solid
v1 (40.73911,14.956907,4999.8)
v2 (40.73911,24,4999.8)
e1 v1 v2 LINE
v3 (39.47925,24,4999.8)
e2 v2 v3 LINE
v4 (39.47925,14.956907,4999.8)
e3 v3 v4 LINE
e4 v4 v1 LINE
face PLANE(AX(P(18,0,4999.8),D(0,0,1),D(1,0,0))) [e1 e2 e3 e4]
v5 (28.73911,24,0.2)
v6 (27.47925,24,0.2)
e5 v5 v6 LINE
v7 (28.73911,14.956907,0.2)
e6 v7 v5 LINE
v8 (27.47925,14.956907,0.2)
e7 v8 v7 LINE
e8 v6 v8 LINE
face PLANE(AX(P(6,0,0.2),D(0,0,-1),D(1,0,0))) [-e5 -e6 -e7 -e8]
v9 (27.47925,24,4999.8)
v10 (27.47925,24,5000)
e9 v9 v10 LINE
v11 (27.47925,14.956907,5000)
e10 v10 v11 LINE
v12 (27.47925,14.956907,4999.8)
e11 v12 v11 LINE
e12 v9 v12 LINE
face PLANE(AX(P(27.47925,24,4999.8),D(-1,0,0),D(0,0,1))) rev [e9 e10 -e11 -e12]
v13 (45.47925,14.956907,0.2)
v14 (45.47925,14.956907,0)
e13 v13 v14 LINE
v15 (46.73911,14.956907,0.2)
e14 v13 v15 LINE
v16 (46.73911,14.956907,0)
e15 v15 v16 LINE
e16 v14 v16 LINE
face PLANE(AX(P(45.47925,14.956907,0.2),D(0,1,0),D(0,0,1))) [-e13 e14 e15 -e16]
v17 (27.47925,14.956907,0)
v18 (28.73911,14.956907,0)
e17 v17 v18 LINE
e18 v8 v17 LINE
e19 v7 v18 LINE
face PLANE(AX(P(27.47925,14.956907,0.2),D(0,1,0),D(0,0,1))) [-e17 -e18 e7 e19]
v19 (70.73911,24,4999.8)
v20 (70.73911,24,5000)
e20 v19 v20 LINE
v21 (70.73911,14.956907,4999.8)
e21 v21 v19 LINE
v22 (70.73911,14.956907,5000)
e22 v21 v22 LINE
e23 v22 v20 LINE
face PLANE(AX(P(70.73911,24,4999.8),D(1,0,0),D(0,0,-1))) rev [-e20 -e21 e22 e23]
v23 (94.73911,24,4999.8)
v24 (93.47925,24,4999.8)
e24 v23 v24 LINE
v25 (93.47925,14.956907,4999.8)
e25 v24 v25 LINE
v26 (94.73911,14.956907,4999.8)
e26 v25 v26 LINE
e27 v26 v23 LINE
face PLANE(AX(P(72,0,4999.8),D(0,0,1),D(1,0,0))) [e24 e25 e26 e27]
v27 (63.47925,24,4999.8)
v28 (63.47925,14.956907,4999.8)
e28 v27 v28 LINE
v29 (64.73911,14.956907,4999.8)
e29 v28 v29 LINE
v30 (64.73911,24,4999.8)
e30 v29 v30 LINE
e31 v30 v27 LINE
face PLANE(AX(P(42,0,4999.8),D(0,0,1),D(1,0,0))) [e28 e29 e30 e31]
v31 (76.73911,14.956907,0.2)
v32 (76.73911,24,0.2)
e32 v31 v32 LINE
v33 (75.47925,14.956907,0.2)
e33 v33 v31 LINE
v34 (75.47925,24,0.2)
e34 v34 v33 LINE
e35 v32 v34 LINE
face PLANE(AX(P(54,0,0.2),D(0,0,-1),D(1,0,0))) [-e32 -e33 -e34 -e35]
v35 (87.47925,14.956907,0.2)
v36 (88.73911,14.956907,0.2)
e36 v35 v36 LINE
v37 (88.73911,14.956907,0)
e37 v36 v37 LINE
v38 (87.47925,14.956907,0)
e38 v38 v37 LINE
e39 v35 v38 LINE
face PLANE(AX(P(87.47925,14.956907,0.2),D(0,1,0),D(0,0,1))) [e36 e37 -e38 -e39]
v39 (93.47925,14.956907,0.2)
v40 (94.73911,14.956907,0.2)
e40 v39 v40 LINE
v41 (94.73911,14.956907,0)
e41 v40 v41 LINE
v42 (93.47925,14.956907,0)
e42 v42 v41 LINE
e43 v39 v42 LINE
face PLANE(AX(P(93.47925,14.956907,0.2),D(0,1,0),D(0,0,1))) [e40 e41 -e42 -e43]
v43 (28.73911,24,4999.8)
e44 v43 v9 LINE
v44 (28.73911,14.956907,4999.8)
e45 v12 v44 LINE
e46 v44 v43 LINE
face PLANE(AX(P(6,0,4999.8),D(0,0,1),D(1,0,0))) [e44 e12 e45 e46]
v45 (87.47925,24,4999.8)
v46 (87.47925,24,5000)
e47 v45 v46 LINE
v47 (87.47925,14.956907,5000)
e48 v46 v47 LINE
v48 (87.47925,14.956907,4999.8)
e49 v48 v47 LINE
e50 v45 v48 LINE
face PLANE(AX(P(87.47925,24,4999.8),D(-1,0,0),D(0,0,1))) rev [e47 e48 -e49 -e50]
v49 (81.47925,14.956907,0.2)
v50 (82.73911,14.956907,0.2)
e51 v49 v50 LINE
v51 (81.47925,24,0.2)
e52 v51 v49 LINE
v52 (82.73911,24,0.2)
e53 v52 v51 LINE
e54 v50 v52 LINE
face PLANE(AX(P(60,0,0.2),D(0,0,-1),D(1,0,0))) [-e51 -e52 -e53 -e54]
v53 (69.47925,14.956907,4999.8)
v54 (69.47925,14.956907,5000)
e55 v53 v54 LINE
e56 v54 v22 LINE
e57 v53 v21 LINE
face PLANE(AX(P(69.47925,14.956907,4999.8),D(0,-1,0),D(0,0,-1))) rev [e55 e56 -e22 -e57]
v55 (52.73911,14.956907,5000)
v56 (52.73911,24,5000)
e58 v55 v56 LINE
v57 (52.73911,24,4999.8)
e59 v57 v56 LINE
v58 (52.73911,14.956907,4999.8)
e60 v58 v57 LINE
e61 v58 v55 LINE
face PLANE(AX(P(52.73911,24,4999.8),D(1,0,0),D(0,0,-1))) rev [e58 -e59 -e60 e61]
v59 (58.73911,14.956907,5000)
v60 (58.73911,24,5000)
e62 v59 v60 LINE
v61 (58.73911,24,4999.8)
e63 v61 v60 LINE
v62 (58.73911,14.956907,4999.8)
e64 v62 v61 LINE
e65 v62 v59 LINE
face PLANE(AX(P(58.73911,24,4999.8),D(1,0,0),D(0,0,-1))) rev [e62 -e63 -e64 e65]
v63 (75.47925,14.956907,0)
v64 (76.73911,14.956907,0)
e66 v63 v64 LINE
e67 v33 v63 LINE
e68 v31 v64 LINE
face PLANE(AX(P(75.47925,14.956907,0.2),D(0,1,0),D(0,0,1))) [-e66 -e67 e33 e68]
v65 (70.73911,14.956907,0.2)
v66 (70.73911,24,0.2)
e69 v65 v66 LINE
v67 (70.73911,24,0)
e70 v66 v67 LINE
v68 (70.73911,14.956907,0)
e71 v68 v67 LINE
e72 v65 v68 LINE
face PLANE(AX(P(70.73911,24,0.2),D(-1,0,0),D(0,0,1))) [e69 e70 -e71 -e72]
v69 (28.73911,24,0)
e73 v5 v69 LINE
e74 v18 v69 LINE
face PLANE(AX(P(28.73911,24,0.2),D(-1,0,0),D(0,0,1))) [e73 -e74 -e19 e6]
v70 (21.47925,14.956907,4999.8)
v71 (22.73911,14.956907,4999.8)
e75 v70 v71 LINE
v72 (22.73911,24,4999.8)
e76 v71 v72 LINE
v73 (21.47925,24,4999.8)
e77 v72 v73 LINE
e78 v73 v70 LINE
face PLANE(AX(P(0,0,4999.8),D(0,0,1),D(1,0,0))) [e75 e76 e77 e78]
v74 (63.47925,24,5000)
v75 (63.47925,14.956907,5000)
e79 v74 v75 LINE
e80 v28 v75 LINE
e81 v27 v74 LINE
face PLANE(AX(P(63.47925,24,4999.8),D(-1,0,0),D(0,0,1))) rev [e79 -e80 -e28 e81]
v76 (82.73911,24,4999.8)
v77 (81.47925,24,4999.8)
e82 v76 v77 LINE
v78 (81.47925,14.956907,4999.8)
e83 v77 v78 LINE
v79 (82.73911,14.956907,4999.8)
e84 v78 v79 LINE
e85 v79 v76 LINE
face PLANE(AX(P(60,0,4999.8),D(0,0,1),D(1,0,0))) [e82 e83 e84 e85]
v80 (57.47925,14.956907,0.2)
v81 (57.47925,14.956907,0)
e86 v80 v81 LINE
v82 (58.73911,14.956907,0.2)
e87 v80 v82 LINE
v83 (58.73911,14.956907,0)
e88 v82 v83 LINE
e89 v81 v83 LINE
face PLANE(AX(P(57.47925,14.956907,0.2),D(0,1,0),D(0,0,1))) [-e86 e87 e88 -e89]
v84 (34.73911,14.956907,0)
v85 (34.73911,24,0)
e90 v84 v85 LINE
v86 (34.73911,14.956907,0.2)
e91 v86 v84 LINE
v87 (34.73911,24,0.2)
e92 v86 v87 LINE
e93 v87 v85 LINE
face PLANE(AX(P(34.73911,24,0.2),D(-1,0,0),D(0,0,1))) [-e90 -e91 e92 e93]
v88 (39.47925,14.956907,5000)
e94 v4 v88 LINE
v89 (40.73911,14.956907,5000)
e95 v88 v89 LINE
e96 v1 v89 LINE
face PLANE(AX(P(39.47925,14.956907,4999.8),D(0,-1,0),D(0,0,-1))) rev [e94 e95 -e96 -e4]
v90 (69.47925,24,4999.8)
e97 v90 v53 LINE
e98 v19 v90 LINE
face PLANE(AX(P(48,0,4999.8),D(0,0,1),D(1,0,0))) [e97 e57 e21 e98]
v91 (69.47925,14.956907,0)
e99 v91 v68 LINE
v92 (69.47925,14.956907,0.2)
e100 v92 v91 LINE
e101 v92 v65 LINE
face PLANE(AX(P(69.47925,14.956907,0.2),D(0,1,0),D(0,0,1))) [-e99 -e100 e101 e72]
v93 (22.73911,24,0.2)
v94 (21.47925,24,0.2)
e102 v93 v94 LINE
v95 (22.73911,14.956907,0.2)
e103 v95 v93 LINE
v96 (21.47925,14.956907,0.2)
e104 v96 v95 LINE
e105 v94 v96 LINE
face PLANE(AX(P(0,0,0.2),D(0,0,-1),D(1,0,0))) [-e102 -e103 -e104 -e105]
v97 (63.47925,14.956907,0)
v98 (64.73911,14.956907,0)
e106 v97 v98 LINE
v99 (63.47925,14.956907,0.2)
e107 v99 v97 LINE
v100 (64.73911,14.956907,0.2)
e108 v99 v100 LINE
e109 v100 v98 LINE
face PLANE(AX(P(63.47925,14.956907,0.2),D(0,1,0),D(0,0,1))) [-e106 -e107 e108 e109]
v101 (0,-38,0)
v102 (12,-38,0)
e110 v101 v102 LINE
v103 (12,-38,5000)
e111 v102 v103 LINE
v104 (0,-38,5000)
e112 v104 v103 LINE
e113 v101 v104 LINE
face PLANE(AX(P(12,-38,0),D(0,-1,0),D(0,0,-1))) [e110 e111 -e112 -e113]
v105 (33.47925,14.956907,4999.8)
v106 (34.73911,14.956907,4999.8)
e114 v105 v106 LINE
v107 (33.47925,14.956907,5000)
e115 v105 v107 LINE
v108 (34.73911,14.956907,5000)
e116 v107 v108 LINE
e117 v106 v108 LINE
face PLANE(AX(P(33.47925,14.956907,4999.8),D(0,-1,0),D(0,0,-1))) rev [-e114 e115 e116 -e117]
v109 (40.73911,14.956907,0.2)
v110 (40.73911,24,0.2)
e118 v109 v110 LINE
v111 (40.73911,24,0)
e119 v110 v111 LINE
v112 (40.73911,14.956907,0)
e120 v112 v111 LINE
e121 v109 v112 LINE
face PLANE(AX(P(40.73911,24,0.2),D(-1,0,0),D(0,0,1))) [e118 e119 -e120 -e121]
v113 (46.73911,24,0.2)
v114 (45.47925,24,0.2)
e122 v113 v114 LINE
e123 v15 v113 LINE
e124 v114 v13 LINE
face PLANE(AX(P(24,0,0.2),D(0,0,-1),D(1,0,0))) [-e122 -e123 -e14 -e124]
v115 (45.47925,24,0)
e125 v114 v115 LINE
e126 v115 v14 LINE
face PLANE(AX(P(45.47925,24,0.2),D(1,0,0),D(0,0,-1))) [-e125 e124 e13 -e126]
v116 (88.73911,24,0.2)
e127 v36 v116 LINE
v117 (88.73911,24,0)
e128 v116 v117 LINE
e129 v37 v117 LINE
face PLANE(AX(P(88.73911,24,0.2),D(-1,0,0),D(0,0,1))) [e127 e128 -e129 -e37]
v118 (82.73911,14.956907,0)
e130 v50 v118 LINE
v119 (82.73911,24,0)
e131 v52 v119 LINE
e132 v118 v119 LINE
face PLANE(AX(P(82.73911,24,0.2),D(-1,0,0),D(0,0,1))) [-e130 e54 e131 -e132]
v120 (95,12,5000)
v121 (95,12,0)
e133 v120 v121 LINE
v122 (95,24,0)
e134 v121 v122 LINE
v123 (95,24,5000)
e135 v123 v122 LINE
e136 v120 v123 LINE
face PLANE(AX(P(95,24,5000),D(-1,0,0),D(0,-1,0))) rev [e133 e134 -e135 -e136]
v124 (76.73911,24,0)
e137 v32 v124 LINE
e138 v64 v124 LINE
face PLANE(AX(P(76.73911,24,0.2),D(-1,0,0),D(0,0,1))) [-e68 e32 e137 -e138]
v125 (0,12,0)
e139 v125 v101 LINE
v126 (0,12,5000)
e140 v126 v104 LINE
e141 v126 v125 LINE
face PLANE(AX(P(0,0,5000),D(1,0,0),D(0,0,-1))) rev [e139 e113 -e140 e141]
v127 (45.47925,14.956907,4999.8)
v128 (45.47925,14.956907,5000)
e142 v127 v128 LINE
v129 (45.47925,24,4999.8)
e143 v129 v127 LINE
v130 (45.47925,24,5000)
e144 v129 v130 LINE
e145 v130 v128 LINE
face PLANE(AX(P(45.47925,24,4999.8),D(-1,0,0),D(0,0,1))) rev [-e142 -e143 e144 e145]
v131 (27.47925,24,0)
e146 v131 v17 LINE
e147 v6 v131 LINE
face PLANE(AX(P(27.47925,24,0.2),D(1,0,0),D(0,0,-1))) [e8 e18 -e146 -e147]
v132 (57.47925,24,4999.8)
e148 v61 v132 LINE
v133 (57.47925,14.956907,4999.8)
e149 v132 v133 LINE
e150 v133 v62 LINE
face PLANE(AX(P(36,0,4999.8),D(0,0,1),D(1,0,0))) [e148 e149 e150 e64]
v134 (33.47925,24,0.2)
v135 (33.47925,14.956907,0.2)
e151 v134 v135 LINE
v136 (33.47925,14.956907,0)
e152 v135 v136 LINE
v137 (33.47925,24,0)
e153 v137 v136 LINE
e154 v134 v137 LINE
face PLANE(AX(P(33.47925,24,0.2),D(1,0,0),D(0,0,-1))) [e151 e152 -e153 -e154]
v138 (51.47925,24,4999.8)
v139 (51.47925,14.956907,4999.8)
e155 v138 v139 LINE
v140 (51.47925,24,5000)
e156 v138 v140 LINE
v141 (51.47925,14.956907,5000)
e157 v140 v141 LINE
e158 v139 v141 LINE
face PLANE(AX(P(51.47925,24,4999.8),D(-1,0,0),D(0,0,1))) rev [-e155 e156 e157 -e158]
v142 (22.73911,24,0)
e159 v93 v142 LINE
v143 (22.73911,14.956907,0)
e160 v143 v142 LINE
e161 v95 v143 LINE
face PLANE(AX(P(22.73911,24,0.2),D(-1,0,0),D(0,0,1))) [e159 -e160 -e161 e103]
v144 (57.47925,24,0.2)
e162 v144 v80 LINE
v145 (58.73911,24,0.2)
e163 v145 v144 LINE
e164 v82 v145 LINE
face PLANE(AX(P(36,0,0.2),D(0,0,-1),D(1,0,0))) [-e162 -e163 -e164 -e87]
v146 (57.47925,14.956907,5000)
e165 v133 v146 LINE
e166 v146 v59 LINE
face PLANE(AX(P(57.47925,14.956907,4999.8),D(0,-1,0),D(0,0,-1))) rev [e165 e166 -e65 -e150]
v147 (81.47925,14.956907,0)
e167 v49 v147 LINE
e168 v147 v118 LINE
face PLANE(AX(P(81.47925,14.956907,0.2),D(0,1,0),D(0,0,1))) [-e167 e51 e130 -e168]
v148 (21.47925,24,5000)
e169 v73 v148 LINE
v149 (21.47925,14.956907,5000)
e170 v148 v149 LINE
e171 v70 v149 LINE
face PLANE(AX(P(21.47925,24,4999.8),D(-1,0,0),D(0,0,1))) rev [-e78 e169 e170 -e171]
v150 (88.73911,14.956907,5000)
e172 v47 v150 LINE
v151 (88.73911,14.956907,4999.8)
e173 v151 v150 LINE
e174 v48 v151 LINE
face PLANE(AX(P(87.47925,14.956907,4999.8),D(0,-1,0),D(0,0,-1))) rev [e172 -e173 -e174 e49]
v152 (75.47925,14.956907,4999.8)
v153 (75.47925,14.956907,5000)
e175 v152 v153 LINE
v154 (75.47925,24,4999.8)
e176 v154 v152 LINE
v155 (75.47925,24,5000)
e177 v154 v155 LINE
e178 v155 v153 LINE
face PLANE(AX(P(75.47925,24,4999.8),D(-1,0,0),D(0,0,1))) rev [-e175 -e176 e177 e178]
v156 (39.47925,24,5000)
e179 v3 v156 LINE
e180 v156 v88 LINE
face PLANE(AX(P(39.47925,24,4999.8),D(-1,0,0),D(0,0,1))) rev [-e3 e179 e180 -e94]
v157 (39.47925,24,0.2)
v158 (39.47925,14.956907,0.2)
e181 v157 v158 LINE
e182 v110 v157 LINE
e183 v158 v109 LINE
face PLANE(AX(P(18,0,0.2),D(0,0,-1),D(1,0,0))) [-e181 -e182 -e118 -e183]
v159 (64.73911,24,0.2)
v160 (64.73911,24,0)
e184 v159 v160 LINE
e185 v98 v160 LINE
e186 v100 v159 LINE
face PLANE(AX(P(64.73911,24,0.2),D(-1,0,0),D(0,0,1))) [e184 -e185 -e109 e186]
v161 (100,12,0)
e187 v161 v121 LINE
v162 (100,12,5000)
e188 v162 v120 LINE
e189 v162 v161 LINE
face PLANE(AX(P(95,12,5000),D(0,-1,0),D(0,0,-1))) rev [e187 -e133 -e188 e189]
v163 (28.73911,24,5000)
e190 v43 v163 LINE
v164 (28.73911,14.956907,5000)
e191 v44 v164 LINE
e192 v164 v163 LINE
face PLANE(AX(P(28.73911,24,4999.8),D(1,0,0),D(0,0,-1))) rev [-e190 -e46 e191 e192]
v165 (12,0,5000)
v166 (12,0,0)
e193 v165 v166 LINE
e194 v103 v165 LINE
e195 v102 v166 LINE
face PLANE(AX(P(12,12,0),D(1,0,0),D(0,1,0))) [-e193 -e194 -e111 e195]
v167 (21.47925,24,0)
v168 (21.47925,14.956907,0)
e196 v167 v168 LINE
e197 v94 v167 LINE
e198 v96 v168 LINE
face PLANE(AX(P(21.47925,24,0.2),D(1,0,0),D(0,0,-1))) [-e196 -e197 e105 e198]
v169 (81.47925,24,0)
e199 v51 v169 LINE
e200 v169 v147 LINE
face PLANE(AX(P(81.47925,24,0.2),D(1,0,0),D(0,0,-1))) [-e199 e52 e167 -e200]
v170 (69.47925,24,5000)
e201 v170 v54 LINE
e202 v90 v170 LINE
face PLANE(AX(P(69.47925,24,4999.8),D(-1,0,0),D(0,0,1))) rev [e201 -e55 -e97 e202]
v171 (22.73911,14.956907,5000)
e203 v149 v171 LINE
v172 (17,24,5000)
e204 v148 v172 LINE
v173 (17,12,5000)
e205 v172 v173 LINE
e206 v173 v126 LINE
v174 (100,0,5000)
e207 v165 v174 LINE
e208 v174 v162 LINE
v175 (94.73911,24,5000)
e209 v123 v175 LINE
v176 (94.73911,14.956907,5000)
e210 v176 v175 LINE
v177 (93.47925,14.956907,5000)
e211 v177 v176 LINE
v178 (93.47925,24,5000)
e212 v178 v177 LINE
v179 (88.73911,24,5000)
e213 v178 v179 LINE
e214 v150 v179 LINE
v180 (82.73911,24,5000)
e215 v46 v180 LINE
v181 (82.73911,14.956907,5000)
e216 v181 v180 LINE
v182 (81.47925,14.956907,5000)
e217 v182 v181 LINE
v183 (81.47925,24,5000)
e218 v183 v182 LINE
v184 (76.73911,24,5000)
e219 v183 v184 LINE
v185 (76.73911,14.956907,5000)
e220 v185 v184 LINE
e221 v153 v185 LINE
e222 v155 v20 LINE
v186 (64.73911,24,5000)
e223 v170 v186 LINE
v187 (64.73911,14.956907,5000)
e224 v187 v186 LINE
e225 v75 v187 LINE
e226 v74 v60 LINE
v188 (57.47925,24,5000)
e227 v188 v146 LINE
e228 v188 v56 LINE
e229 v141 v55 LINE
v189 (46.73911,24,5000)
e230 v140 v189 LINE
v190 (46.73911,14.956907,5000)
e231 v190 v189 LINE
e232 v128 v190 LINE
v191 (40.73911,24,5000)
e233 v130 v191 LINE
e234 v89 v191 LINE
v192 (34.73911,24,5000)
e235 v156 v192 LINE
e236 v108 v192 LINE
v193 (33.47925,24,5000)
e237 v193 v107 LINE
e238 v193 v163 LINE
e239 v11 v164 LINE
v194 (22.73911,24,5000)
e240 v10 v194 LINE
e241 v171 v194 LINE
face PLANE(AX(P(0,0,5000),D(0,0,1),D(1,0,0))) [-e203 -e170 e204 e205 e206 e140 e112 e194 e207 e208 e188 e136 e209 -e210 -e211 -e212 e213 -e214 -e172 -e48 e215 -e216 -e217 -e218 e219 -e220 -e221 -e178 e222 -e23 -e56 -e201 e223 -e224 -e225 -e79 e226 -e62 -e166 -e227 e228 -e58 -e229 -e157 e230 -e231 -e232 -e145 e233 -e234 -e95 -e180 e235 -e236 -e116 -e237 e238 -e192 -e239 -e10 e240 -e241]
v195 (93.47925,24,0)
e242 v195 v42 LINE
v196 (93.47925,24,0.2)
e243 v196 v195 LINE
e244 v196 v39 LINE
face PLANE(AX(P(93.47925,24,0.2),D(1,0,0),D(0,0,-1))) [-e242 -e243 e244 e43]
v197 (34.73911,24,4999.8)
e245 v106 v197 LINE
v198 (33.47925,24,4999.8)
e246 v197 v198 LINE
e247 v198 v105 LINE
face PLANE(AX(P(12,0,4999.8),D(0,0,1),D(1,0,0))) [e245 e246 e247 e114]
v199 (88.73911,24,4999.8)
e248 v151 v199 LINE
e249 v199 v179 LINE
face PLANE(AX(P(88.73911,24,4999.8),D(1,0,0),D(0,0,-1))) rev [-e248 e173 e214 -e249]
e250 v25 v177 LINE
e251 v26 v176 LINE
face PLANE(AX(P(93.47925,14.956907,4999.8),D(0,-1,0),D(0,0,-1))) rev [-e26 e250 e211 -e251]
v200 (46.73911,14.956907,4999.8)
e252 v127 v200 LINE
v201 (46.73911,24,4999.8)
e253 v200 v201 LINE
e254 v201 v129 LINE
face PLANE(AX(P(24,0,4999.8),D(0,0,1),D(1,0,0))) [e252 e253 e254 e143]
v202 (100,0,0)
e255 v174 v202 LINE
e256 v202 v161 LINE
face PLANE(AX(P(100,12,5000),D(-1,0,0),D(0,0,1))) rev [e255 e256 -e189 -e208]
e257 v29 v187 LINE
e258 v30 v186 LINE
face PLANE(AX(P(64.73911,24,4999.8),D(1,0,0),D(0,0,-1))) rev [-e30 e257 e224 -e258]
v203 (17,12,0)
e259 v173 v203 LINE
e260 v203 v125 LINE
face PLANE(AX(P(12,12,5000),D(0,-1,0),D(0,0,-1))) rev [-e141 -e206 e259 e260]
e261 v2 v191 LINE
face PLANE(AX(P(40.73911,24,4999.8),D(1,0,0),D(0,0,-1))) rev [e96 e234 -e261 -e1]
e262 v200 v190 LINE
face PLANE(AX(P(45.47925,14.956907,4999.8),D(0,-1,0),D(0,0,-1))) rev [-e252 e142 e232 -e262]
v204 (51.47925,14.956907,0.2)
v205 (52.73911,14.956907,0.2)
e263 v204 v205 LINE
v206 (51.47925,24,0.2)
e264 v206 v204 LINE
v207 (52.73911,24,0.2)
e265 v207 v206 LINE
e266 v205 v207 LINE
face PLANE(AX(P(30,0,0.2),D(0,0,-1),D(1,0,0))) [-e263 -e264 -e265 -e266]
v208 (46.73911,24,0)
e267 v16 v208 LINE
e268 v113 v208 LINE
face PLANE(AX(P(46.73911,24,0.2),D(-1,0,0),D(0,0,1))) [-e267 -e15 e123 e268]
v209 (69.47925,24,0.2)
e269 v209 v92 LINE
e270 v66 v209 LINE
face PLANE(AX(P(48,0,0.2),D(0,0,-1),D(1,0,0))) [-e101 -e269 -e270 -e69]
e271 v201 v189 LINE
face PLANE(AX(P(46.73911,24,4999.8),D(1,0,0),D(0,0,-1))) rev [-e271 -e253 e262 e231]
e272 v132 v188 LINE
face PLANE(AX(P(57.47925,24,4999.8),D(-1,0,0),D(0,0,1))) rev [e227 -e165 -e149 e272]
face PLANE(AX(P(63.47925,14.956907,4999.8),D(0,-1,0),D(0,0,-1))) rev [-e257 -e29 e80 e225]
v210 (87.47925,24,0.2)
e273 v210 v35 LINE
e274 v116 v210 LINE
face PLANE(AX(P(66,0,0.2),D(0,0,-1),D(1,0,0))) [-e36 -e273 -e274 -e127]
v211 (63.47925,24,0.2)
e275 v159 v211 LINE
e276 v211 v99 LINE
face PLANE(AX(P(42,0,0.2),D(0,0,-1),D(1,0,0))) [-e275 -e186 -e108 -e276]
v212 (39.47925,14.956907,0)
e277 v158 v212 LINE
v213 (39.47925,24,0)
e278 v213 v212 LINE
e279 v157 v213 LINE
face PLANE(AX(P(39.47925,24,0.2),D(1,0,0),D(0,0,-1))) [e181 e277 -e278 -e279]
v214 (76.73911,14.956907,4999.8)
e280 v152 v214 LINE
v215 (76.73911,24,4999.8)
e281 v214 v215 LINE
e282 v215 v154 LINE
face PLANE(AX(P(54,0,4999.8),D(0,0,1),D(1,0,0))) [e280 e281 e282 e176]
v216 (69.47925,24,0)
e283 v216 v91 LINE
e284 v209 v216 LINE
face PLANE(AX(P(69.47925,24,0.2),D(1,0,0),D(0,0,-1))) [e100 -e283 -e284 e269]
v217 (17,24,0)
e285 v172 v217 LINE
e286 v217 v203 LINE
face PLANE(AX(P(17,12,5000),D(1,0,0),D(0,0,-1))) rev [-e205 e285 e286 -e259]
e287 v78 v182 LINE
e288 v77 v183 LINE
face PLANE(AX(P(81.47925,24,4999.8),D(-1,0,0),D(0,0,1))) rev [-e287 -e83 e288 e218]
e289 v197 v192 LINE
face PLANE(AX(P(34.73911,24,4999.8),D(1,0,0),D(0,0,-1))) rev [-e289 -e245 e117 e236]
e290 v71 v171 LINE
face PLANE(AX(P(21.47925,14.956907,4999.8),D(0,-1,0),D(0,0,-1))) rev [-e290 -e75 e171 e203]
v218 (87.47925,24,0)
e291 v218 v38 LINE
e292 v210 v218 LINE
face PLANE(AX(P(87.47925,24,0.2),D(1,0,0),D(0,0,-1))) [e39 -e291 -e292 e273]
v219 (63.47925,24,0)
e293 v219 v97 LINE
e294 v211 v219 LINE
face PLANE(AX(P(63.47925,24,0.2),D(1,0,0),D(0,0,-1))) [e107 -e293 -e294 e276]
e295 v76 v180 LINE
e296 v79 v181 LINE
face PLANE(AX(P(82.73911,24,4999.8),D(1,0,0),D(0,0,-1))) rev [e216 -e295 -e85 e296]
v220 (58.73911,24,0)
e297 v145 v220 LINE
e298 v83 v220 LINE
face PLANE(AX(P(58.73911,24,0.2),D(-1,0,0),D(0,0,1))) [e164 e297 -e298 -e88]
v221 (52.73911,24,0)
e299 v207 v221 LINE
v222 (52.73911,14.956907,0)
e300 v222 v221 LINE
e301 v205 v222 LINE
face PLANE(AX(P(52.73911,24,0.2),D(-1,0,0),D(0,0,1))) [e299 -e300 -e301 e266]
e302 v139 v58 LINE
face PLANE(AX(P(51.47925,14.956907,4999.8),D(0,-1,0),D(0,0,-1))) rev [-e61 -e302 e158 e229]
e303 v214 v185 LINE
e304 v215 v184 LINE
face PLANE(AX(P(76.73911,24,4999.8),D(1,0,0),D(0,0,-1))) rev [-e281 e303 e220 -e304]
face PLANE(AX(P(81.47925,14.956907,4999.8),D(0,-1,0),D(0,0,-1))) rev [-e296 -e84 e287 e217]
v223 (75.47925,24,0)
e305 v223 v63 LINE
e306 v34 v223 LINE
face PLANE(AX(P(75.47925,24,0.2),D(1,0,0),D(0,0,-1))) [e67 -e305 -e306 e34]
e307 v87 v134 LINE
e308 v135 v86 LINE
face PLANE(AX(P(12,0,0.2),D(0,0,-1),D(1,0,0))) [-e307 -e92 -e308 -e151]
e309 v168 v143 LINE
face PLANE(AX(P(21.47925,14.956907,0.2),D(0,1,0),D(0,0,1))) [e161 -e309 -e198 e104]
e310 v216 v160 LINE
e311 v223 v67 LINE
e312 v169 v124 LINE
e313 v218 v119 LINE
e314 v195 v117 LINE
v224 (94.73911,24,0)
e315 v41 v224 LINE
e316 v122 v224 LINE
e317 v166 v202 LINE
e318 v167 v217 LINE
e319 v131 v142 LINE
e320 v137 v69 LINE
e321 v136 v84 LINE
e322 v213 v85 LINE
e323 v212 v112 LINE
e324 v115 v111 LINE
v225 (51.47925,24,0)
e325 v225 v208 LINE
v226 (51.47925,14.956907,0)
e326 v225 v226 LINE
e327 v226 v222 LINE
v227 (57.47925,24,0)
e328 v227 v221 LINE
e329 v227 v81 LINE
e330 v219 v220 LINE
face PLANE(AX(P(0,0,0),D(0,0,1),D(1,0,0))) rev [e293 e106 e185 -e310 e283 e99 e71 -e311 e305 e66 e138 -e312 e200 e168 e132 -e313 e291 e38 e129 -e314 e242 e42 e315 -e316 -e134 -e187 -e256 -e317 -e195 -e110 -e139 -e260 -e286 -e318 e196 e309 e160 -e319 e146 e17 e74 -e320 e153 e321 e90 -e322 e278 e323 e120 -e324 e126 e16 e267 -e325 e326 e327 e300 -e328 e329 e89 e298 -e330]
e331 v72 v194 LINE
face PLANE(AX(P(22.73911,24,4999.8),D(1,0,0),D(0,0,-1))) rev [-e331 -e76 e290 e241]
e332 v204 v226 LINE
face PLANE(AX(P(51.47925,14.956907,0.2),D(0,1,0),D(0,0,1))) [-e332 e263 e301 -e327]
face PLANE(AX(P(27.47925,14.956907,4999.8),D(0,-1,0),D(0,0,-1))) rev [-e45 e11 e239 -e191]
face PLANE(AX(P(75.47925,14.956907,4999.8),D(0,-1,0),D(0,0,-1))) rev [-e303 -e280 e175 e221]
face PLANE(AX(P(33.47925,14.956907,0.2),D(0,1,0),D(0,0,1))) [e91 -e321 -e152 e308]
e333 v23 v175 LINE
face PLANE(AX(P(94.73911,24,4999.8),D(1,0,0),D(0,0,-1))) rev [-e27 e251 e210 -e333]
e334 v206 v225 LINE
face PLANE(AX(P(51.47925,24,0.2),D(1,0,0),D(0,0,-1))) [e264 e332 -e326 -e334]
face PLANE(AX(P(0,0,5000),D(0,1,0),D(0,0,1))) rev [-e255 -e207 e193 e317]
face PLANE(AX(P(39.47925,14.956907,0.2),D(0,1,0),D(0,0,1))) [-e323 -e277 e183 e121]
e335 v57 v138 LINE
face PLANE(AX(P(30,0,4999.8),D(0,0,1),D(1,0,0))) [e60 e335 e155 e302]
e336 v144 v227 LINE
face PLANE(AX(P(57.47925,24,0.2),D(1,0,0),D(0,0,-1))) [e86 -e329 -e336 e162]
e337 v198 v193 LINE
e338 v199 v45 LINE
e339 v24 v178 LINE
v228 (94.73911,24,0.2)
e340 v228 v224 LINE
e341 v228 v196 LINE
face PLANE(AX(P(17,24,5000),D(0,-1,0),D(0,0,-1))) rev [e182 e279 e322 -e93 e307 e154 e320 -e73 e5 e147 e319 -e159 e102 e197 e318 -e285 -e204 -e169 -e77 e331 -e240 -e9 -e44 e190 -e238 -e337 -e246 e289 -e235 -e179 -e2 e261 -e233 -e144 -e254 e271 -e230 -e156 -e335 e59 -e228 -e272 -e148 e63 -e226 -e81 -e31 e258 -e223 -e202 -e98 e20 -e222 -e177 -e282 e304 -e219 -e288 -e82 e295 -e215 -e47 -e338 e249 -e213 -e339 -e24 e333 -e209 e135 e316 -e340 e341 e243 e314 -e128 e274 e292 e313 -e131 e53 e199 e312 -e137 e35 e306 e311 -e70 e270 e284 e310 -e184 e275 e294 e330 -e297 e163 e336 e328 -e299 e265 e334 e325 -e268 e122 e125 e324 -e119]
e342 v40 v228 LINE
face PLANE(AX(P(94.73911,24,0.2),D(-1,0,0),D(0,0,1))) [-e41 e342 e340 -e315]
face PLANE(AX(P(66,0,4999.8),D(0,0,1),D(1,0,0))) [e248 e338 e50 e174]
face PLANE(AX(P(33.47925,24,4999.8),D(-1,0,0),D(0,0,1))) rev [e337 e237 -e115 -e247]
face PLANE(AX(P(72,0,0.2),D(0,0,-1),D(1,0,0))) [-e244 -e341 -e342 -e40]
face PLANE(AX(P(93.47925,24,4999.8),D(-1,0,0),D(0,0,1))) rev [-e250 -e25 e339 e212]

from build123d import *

# Parameters (mm, degrees)
BOSS_EXTRUDE1_DEPTH      = 5000
SKETCH2_W                = 1.259860676
SKETCH2_H                = 9.043092937
CUT_EXTRUDE1_DEPTH       = 0.2
LPATTERN1_COUNT          = 16
LPATTERN1_PITCH          = 6
MIRROR1_COPY_1_SKETCH_W  = 1.259860676
MIRROR1_COPY_1_SKETCH_H  = 9.043092937
MIRROR1_COPY_1_DEPTH     = 0.2
MIRROR1_COPY_2_SKETCH_W  = 1.259860676
MIRROR1_COPY_2_SKETCH_H  = 9.043092937
MIRROR1_COPY_2_DEPTH     = 0.2
MIRROR1_COPY_3_SKETCH_W  = 1.259860676
MIRROR1_COPY_3_SKETCH_H  = 9.043092937
MIRROR1_COPY_3_DEPTH     = 0.2
MIRROR1_COPY_4_SKETCH_W  = 1.259860676
MIRROR1_COPY_4_SKETCH_H  = 9.043092937
MIRROR1_COPY_4_DEPTH     = 0.2
MIRROR1_COPY_5_SKETCH_W  = 1.259860676
MIRROR1_COPY_5_SKETCH_H  = 9.043092937
MIRROR1_COPY_5_DEPTH     = 0.2
MIRROR1_COPY_6_SKETCH_W  = 1.259860676
MIRROR1_COPY_6_SKETCH_H  = 9.043092937
MIRROR1_COPY_6_DEPTH     = 0.2
MIRROR1_COPY_7_SKETCH_W  = 1.259860676
MIRROR1_COPY_7_SKETCH_H  = 9.043092937
MIRROR1_COPY_7_DEPTH     = 0.2
MIRROR1_COPY_8_SKETCH_W  = 1.259860676
MIRROR1_COPY_8_SKETCH_H  = 9.043092937
MIRROR1_COPY_8_DEPTH     = 0.2
MIRROR1_COPY_9_SKETCH_W  = 1.259860676
MIRROR1_COPY_9_SKETCH_H  = 9.043092937
MIRROR1_COPY_9_DEPTH     = 0.2
MIRROR1_COPY_10_SKETCH_W = 1.259860676
MIRROR1_COPY_10_SKETCH_H = 9.043092937
MIRROR1_COPY_10_DEPTH    = 0.2
MIRROR1_COPY_11_SKETCH_W = 1.259860676
MIRROR1_COPY_11_SKETCH_H = 9.043092937
MIRROR1_COPY_11_DEPTH    = 0.2
MIRROR1_COPY_12_SKETCH_W = 1.259860676
MIRROR1_COPY_12_SKETCH_H = 9.043092937
MIRROR1_COPY_12_DEPTH    = 0.2
MIRROR1_COPY_13_SKETCH_W = 1.259860676
MIRROR1_COPY_13_SKETCH_H = 9.043092937
MIRROR1_COPY_13_DEPTH    = 0.2
MIRROR1_COPY_14_SKETCH_W = 1.259860676
MIRROR1_COPY_14_SKETCH_H = 9.043092937
MIRROR1_COPY_14_DEPTH    = 0.2
MIRROR1_COPY_15_SKETCH_W = 1.259860676
MIRROR1_COPY_15_SKETCH_H = 9.043092937
MIRROR1_COPY_15_DEPTH    = 0.2
SKETCH3_W                = 12
SKETCH3_H                = 50
BOSS_EXTRUDE2_DEPTH      = 5000
SKETCH4_W                = 12
SKETCH4_H                = 88
CUT_EXTRUDE2_DEPTH       = 5002.99960016


with BuildPart() as part:
    # Sketch1 → Boss-Extrude1 (new body)
    with BuildSketch(Plane.XY):
        Polygon((0, 0), (100, 0), (100, 12), (95, 12), (95, 24), (17, 24), (17, 12), (12, 12), (12, 100), (0, 100), align=None)
    extrude(amount=BOSS_EXTRUDE1_DEPTH)

    # Sketch2 → Cut-Extrude1 (cut)
    with BuildSketch(Plane.XY.offset(5000)):
        with Locations((22.109179897, 19.478453532)):
            Rectangle(SKETCH2_W, SKETCH2_H)
    cut_extrude1 = extrude(amount=-CUT_EXTRUDE1_DEPTH, mode=Mode.SUBTRACT)

    # LPattern1: Cut-Extrude1 ×16
    with Locations(*[(i * LPATTERN1_PITCH, 0, 0) for i in range(1, LPATTERN1_COUNT)]):
        add(cut_extrude1, mode=Mode.SUBTRACT)

    # Mirror1: Cut-Extrude1 across plane
    add(cut_extrude1.mirror(Plane(origin=(0, 0, 2500), x_dir=(1, 0, 0), z_dir=(0, 0, -1))), mode=Mode.SUBTRACT)

    # Mirror1 copy 1 sketch → Mirror1 copy 1 (cut)
    with BuildSketch(Plane(origin=(6, 0, 0), x_dir=(1, 0, 0), z_dir=(0, 0, -1))):
        with Locations((22.109179897, -19.478453532)):
            Rectangle(MIRROR1_COPY_1_SKETCH_W, MIRROR1_COPY_1_SKETCH_H)
    extrude(amount=-MIRROR1_COPY_1_DEPTH, mode=Mode.SUBTRACT)

    # Mirror1 copy 2 sketch → Mirror1 copy 2 (cut)
    with BuildSketch(Plane(origin=(12, 0, 0), x_dir=(1, 0, 0), z_dir=(0, 0, -1))):
        with Locations((22.109179897, -19.478453532)):
            Rectangle(MIRROR1_COPY_2_SKETCH_W, MIRROR1_COPY_2_SKETCH_H)
    extrude(amount=-MIRROR1_COPY_2_DEPTH, mode=Mode.SUBTRACT)

    # Mirror1 copy 3 sketch → Mirror1 copy 3 (cut)
    with BuildSketch(Plane(origin=(18, 0, 0), x_dir=(1, 0, 0), z_dir=(0, 0, -1))):
        with Locations((22.109179897, -19.478453532)):
            Rectangle(MIRROR1_COPY_3_SKETCH_W, MIRROR1_COPY_3_SKETCH_H)
    extrude(amount=-MIRROR1_COPY_3_DEPTH, mode=Mode.SUBTRACT)

    # Mirror1 copy 4 sketch → Mirror1 copy 4 (cut)
    with BuildSketch(Plane(origin=(24, 0, 0), x_dir=(1, 0, 0), z_dir=(0, 0, -1))):
        with Locations((22.109179897, -19.478453532)):
            Rectangle(MIRROR1_COPY_4_SKETCH_W, MIRROR1_COPY_4_SKETCH_H)
    extrude(amount=-MIRROR1_COPY_4_DEPTH, mode=Mode.SUBTRACT)

    # Mirror1 copy 5 sketch → Mirror1 copy 5 (cut)
    with BuildSketch(Plane(origin=(30, 0, 0), x_dir=(1, 0, 0), z_dir=(0, 0, -1))):
        with Locations((22.109179897, -19.478453532)):
            Rectangle(MIRROR1_COPY_5_SKETCH_W, MIRROR1_COPY_5_SKETCH_H)
    extrude(amount=-MIRROR1_COPY_5_DEPTH, mode=Mode.SUBTRACT)

    # Mirror1 copy 6 sketch → Mirror1 copy 6 (cut)
    with BuildSketch(Plane(origin=(36, 0, 0), x_dir=(1, 0, 0), z_dir=(0, 0, -1))):
        with Locations((22.109179897, -19.478453532)):
            Rectangle(MIRROR1_COPY_6_SKETCH_W, MIRROR1_COPY_6_SKETCH_H)
    extrude(amount=-MIRROR1_COPY_6_DEPTH, mode=Mode.SUBTRACT)

    # Mirror1 copy 7 sketch → Mirror1 copy 7 (cut)
    with BuildSketch(Plane(origin=(42, 0, 0), x_dir=(1, 0, 0), z_dir=(0, 0, -1))):
        with Locations((22.109179897, -19.478453532)):
            Rectangle(MIRROR1_COPY_7_SKETCH_W, MIRROR1_COPY_7_SKETCH_H)
    extrude(amount=-MIRROR1_COPY_7_DEPTH, mode=Mode.SUBTRACT)

    # Mirror1 copy 8 sketch → Mirror1 copy 8 (cut)
    with BuildSketch(Plane(origin=(48, 0, 0), x_dir=(1, 0, 0), z_dir=(0, 0, -1))):
        with Locations((22.109179897, -19.478453532)):
            Rectangle(MIRROR1_COPY_8_SKETCH_W, MIRROR1_COPY_8_SKETCH_H)
    extrude(amount=-MIRROR1_COPY_8_DEPTH, mode=Mode.SUBTRACT)

    # Mirror1 copy 9 sketch → Mirror1 copy 9 (cut)
    with BuildSketch(Plane(origin=(54, 0, 0), x_dir=(1, 0, 0), z_dir=(0, 0, -1))):
        with Locations((22.109179897, -19.478453532)):
            Rectangle(MIRROR1_COPY_9_SKETCH_W, MIRROR1_COPY_9_SKETCH_H)
    extrude(amount=-MIRROR1_COPY_9_DEPTH, mode=Mode.SUBTRACT)

    # Mirror1 copy 10 sketch → Mirror1 copy 10 (cut)
    with BuildSketch(Plane(origin=(60, 0, 0), x_dir=(1, 0, 0), z_dir=(0, 0, -1))):
        with Locations((22.109179897, -19.478453532)):
            Rectangle(MIRROR1_COPY_10_SKETCH_W, MIRROR1_COPY_10_SKETCH_H)
    extrude(amount=-MIRROR1_COPY_10_DEPTH, mode=Mode.SUBTRACT)

    # Mirror1 copy 11 sketch → Mirror1 copy 11 (cut)
    with BuildSketch(Plane(origin=(66, 0, 0), x_dir=(1, 0, 0), z_dir=(0, 0, -1))):
        with Locations((22.109179897, -19.478453532)):
            Rectangle(MIRROR1_COPY_11_SKETCH_W, MIRROR1_COPY_11_SKETCH_H)
    extrude(amount=-MIRROR1_COPY_11_DEPTH, mode=Mode.SUBTRACT)

    # Mirror1 copy 12 sketch → Mirror1 copy 12 (cut)
    with BuildSketch(Plane(origin=(72, 0, 0), x_dir=(1, 0, 0), z_dir=(0, 0, -1))):
        with Locations((22.109179897, -19.478453532)):
            Rectangle(MIRROR1_COPY_12_SKETCH_W, MIRROR1_COPY_12_SKETCH_H)
    extrude(amount=-MIRROR1_COPY_12_DEPTH, mode=Mode.SUBTRACT)

    # Mirror1 copy 13 sketch → Mirror1 copy 13 (cut)
    with BuildSketch(Plane(origin=(78, 0, 0), x_dir=(1, 0, 0), z_dir=(0, 0, -1))):
        with Locations((22.109179897, -19.478453532)):
            Rectangle(MIRROR1_COPY_13_SKETCH_W, MIRROR1_COPY_13_SKETCH_H)
    extrude(amount=-MIRROR1_COPY_13_DEPTH, mode=Mode.SUBTRACT)

    # Mirror1 copy 14 sketch → Mirror1 copy 14 (cut)
    with BuildSketch(Plane(origin=(84, 0, 0), x_dir=(1, 0, 0), z_dir=(0, 0, -1))):
        with Locations((22.109179897, -19.478453532)):
            Rectangle(MIRROR1_COPY_14_SKETCH_W, MIRROR1_COPY_14_SKETCH_H)
    extrude(amount=-MIRROR1_COPY_14_DEPTH, mode=Mode.SUBTRACT)

    # Mirror1 copy 15 sketch → Mirror1 copy 15 (cut)
    with BuildSketch(Plane(origin=(90, 0, 0), x_dir=(1, 0, 0), z_dir=(0, 0, -1))):
        with Locations((22.109179897, -19.478453532)):
            Rectangle(MIRROR1_COPY_15_SKETCH_W, MIRROR1_COPY_15_SKETCH_H)
    extrude(amount=-MIRROR1_COPY_15_DEPTH, mode=Mode.SUBTRACT)

    # Sketch3 → Boss-Extrude2 (add)
    with BuildSketch(Plane.XY.offset(5000)):
        with Locations((6, -13)):
            Rectangle(SKETCH3_W, SKETCH3_H)
    extrude(amount=-BOSS_EXTRUDE2_DEPTH)

    # Sketch4 → Cut-Extrude2 (cut, through all)
    with BuildSketch(Plane(origin=(0, 0, 0), x_dir=(-1, 0, 0), z_dir=(0, 0, -1))):
        with Locations((-6, 56)):
            Rectangle(SKETCH4_W, SKETCH4_H)
    extrude(amount=-CUT_EXTRUDE2_DEPTH, mode=Mode.SUBTRACT)


solid = part.part
